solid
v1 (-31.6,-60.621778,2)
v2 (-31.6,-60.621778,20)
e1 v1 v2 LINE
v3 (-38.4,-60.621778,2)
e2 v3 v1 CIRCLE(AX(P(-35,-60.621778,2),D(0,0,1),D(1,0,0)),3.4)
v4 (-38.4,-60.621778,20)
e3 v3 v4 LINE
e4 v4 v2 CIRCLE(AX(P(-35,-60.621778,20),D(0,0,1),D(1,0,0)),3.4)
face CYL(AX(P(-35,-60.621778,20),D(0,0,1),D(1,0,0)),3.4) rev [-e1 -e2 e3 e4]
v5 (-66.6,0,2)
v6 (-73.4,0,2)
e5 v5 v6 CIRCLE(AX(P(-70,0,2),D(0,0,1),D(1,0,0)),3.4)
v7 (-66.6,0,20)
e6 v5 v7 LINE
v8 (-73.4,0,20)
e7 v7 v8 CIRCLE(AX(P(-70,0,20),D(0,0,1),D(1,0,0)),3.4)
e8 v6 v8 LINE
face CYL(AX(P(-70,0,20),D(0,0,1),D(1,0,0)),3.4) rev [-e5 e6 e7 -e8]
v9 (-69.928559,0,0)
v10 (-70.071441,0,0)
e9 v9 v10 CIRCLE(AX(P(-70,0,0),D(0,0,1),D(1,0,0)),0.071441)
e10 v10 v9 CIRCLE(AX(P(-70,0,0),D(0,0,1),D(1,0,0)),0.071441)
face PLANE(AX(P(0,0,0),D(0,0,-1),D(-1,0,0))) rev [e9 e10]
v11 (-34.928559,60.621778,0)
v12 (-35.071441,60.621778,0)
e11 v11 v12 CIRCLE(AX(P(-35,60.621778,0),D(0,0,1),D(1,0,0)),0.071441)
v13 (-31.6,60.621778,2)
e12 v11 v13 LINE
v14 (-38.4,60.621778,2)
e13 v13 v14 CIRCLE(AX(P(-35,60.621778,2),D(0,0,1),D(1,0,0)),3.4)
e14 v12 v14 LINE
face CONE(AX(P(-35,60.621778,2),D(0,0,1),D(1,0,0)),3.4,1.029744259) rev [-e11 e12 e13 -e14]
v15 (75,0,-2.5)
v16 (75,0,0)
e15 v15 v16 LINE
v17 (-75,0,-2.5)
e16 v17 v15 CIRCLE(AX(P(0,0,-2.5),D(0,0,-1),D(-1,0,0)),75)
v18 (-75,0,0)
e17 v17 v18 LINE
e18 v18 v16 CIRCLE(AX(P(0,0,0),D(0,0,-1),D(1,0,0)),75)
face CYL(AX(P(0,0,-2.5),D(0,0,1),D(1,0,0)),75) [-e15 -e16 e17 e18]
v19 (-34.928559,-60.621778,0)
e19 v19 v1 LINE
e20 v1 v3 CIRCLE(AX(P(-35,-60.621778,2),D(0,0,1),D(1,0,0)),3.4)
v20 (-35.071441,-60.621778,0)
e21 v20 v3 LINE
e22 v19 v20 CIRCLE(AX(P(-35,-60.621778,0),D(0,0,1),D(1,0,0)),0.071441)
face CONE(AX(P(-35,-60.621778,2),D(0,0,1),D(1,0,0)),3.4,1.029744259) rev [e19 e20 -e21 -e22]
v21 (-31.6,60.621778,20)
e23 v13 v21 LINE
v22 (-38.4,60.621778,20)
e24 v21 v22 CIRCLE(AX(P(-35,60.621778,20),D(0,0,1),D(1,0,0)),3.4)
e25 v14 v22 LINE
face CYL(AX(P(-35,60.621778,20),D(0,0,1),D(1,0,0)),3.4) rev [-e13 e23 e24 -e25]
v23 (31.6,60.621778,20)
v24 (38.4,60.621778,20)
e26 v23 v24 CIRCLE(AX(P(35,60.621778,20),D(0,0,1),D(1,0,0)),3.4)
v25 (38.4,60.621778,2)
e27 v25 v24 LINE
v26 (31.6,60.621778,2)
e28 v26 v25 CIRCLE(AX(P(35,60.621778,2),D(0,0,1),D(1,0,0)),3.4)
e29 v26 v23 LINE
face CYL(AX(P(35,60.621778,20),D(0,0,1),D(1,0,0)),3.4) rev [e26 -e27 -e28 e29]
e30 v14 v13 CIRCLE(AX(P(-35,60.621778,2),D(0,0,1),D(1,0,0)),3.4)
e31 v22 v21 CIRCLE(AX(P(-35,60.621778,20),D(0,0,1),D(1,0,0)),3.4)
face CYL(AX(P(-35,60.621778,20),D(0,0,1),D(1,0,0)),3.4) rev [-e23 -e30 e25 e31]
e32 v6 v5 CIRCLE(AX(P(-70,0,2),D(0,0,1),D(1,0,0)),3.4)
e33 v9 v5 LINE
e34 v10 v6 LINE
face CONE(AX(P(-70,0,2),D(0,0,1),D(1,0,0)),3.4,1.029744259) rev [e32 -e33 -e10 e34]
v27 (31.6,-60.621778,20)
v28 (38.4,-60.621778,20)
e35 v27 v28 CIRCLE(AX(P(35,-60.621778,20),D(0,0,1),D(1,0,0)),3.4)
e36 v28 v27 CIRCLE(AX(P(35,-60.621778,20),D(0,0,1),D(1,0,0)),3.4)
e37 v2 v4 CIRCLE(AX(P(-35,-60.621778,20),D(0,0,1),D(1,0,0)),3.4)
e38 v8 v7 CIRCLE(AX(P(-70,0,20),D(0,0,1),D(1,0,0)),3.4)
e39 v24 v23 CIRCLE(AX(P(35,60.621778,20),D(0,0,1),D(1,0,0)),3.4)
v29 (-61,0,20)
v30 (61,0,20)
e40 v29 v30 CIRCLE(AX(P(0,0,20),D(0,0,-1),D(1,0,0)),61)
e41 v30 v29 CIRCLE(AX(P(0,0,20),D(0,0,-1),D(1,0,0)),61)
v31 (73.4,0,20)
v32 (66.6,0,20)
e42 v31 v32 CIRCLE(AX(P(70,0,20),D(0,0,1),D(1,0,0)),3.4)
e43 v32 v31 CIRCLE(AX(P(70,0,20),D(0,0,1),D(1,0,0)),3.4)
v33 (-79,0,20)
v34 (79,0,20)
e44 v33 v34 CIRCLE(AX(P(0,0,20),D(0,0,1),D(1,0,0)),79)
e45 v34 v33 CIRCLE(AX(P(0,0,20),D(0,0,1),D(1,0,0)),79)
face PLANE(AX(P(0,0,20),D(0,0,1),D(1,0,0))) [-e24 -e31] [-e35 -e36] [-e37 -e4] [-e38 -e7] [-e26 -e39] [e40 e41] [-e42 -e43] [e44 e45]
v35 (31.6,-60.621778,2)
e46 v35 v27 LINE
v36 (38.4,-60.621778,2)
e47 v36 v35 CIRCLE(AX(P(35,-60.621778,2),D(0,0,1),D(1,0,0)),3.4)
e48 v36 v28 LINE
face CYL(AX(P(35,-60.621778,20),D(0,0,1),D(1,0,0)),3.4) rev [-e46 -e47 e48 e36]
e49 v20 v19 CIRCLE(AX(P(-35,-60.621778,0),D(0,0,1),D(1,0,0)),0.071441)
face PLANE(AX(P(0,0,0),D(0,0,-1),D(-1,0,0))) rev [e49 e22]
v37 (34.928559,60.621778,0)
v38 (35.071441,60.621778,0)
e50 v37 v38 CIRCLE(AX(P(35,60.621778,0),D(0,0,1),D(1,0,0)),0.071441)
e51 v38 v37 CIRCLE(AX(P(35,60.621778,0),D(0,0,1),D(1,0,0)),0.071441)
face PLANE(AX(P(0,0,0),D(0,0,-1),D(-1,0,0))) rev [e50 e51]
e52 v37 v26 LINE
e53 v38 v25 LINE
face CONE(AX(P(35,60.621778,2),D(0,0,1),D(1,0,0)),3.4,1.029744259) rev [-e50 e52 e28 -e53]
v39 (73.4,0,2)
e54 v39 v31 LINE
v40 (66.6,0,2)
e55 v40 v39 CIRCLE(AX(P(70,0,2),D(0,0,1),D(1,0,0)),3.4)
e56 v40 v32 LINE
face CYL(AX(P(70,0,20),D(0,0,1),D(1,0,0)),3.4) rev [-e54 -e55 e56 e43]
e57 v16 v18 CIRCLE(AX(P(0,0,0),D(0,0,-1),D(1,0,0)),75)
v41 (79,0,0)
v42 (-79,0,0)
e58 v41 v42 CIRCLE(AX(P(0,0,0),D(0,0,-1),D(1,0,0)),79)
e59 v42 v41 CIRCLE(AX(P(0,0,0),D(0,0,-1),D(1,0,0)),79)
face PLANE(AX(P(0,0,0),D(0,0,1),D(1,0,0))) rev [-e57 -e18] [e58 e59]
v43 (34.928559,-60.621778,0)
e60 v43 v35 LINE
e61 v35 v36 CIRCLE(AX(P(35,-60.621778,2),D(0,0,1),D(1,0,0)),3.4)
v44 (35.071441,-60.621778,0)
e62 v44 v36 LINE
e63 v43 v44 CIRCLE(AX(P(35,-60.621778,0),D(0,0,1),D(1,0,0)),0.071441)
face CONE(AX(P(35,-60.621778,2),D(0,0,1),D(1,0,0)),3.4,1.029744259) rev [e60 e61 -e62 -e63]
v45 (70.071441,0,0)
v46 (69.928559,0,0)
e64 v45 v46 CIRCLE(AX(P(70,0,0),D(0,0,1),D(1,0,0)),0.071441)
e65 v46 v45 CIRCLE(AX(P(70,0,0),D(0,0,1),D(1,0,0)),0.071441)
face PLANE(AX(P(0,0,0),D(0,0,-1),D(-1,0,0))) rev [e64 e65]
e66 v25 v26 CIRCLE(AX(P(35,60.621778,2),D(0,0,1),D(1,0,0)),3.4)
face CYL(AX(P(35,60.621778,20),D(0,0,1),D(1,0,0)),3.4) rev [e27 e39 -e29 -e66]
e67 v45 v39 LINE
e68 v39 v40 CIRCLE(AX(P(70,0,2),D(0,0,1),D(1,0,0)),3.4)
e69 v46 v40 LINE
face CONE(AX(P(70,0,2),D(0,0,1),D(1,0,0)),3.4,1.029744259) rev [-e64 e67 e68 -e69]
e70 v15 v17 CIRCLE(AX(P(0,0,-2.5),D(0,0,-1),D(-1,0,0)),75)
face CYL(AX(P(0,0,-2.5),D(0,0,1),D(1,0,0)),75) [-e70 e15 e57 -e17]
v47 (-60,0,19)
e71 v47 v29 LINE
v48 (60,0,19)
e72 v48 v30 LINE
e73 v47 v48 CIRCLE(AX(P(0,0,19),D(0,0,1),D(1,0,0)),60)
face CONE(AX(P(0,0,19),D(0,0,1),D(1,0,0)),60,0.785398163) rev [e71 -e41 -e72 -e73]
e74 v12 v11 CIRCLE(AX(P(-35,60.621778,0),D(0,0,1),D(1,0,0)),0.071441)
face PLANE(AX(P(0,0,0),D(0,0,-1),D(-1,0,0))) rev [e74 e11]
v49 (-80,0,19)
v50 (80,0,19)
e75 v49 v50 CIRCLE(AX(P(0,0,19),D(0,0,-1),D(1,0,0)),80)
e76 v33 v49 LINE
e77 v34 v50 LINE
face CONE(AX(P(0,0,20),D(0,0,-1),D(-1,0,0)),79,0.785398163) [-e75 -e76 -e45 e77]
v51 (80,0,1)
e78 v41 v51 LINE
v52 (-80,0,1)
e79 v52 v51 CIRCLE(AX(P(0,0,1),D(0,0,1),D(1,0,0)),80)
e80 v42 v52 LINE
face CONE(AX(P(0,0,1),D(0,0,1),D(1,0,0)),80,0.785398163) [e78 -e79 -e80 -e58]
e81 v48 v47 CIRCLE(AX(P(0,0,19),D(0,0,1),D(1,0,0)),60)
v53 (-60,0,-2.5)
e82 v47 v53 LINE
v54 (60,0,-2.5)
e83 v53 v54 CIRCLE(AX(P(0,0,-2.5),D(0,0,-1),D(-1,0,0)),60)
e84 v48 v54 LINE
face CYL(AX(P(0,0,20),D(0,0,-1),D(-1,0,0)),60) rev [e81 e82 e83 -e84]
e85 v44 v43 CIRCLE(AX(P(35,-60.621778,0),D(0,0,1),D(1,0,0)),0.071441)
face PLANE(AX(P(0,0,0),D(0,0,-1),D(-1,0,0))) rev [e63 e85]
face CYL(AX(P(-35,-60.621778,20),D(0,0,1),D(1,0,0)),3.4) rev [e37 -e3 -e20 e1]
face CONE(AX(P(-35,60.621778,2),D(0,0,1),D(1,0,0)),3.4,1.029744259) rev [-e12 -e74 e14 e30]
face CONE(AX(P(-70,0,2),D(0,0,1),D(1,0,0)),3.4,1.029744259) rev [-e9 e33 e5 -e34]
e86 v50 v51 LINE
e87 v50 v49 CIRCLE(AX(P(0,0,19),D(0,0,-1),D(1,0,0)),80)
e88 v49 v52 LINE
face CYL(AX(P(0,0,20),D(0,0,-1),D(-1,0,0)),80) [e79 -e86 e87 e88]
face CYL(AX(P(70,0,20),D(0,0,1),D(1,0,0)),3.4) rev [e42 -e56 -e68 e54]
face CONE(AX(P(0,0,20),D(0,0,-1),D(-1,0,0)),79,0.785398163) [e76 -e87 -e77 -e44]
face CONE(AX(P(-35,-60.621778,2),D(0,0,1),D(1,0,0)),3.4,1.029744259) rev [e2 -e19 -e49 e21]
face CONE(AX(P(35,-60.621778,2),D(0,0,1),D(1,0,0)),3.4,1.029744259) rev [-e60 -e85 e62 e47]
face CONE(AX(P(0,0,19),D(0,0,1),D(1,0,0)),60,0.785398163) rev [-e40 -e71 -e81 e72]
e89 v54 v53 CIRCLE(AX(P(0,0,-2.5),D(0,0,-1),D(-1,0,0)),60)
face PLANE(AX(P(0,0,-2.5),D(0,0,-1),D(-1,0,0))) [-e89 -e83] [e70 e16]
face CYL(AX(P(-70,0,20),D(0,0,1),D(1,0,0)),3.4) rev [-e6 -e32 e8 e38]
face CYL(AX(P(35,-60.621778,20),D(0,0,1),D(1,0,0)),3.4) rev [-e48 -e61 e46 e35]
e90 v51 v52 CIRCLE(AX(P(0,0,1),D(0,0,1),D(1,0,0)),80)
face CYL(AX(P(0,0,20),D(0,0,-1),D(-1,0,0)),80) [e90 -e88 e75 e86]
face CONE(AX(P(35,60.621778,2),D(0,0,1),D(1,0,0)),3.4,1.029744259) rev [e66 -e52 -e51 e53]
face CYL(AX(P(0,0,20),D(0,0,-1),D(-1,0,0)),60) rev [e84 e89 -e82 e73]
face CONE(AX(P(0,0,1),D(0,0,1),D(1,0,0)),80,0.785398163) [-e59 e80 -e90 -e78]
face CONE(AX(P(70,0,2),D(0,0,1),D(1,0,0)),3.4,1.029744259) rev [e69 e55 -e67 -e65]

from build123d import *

# Parameters (mm, degrees)
SKETCH1_R                  = 80
SKETCH1_R_2                = 60
BOSS_EXTRUDE1_DEPTH        = 20
M8X1_25_TAPPED_HOLE2_D     = 6.8
M8X1_25_TAPPED_HOLE2_DEPTH = 18
M8X1_25_TAPPED_HOLE2_TIP   = 2.042926105
CHAMFER1_SIZE              = 1
BOSS_EXTRUDE2_START        = 2.5
SKETCH6_R                  = 75
SKETCH6_R_2                = 60
BOSS_EXTRUDE2_DEPTH        = 2.5


with BuildPart() as part:
    # Sketch1 → Boss-Extrude1 (new body)
    with BuildSketch(Plane.XY):
        Circle(SKETCH1_R)
        Circle(SKETCH1_R_2, mode=Mode.SUBTRACT)
    extrude(amount=BOSS_EXTRUDE1_DEPTH)

    # M8x1.25 Tapped Hole2
    with Locations(Plane(origin=(-35, 60.621778265, 20), x_dir=(1, 0, 0), z_dir=(0, 0, 1))):
        with Locations((0, 0), (-35, -60.621778265), (0, -121.24355653), (70, -121.24355653), (105, -60.621778265), (70, 0)):
            Hole(M8X1_25_TAPPED_HOLE2_D / 2, depth=M8X1_25_TAPPED_HOLE2_DEPTH)
            with Locations((0, 0, -(M8X1_25_TAPPED_HOLE2_DEPTH + M8X1_25_TAPPED_HOLE2_TIP / 2))):  # 118° drill point
                Cone(0, M8X1_25_TAPPED_HOLE2_D / 2, M8X1_25_TAPPED_HOLE2_TIP, mode=Mode.SUBTRACT)

    # Chamfer1
    chamfer1_edges = [part.edges().sort_by_distance(p)[0] for p in [
        (-80, 0, 0),
        (-80, 0, 20),
        (-60, 0, 20),
    ]]
    chamfer(chamfer1_edges, length=CHAMFER1_SIZE)

    # Sketch6 → Boss-Extrude2 (add)
    with BuildSketch(Plane(origin=(0, 0, 0), x_dir=(-1, 0, 0), z_dir=(0, 0, -1)).offset(BOSS_EXTRUDE2_START)):
        with Locations(Location((0, 0, 0), (0, 0, 180))):
            Circle(SKETCH6_R)
        Circle(SKETCH6_R_2, mode=Mode.SUBTRACT)
    extrude(amount=-BOSS_EXTRUDE2_DEPTH)


solid = part.part
